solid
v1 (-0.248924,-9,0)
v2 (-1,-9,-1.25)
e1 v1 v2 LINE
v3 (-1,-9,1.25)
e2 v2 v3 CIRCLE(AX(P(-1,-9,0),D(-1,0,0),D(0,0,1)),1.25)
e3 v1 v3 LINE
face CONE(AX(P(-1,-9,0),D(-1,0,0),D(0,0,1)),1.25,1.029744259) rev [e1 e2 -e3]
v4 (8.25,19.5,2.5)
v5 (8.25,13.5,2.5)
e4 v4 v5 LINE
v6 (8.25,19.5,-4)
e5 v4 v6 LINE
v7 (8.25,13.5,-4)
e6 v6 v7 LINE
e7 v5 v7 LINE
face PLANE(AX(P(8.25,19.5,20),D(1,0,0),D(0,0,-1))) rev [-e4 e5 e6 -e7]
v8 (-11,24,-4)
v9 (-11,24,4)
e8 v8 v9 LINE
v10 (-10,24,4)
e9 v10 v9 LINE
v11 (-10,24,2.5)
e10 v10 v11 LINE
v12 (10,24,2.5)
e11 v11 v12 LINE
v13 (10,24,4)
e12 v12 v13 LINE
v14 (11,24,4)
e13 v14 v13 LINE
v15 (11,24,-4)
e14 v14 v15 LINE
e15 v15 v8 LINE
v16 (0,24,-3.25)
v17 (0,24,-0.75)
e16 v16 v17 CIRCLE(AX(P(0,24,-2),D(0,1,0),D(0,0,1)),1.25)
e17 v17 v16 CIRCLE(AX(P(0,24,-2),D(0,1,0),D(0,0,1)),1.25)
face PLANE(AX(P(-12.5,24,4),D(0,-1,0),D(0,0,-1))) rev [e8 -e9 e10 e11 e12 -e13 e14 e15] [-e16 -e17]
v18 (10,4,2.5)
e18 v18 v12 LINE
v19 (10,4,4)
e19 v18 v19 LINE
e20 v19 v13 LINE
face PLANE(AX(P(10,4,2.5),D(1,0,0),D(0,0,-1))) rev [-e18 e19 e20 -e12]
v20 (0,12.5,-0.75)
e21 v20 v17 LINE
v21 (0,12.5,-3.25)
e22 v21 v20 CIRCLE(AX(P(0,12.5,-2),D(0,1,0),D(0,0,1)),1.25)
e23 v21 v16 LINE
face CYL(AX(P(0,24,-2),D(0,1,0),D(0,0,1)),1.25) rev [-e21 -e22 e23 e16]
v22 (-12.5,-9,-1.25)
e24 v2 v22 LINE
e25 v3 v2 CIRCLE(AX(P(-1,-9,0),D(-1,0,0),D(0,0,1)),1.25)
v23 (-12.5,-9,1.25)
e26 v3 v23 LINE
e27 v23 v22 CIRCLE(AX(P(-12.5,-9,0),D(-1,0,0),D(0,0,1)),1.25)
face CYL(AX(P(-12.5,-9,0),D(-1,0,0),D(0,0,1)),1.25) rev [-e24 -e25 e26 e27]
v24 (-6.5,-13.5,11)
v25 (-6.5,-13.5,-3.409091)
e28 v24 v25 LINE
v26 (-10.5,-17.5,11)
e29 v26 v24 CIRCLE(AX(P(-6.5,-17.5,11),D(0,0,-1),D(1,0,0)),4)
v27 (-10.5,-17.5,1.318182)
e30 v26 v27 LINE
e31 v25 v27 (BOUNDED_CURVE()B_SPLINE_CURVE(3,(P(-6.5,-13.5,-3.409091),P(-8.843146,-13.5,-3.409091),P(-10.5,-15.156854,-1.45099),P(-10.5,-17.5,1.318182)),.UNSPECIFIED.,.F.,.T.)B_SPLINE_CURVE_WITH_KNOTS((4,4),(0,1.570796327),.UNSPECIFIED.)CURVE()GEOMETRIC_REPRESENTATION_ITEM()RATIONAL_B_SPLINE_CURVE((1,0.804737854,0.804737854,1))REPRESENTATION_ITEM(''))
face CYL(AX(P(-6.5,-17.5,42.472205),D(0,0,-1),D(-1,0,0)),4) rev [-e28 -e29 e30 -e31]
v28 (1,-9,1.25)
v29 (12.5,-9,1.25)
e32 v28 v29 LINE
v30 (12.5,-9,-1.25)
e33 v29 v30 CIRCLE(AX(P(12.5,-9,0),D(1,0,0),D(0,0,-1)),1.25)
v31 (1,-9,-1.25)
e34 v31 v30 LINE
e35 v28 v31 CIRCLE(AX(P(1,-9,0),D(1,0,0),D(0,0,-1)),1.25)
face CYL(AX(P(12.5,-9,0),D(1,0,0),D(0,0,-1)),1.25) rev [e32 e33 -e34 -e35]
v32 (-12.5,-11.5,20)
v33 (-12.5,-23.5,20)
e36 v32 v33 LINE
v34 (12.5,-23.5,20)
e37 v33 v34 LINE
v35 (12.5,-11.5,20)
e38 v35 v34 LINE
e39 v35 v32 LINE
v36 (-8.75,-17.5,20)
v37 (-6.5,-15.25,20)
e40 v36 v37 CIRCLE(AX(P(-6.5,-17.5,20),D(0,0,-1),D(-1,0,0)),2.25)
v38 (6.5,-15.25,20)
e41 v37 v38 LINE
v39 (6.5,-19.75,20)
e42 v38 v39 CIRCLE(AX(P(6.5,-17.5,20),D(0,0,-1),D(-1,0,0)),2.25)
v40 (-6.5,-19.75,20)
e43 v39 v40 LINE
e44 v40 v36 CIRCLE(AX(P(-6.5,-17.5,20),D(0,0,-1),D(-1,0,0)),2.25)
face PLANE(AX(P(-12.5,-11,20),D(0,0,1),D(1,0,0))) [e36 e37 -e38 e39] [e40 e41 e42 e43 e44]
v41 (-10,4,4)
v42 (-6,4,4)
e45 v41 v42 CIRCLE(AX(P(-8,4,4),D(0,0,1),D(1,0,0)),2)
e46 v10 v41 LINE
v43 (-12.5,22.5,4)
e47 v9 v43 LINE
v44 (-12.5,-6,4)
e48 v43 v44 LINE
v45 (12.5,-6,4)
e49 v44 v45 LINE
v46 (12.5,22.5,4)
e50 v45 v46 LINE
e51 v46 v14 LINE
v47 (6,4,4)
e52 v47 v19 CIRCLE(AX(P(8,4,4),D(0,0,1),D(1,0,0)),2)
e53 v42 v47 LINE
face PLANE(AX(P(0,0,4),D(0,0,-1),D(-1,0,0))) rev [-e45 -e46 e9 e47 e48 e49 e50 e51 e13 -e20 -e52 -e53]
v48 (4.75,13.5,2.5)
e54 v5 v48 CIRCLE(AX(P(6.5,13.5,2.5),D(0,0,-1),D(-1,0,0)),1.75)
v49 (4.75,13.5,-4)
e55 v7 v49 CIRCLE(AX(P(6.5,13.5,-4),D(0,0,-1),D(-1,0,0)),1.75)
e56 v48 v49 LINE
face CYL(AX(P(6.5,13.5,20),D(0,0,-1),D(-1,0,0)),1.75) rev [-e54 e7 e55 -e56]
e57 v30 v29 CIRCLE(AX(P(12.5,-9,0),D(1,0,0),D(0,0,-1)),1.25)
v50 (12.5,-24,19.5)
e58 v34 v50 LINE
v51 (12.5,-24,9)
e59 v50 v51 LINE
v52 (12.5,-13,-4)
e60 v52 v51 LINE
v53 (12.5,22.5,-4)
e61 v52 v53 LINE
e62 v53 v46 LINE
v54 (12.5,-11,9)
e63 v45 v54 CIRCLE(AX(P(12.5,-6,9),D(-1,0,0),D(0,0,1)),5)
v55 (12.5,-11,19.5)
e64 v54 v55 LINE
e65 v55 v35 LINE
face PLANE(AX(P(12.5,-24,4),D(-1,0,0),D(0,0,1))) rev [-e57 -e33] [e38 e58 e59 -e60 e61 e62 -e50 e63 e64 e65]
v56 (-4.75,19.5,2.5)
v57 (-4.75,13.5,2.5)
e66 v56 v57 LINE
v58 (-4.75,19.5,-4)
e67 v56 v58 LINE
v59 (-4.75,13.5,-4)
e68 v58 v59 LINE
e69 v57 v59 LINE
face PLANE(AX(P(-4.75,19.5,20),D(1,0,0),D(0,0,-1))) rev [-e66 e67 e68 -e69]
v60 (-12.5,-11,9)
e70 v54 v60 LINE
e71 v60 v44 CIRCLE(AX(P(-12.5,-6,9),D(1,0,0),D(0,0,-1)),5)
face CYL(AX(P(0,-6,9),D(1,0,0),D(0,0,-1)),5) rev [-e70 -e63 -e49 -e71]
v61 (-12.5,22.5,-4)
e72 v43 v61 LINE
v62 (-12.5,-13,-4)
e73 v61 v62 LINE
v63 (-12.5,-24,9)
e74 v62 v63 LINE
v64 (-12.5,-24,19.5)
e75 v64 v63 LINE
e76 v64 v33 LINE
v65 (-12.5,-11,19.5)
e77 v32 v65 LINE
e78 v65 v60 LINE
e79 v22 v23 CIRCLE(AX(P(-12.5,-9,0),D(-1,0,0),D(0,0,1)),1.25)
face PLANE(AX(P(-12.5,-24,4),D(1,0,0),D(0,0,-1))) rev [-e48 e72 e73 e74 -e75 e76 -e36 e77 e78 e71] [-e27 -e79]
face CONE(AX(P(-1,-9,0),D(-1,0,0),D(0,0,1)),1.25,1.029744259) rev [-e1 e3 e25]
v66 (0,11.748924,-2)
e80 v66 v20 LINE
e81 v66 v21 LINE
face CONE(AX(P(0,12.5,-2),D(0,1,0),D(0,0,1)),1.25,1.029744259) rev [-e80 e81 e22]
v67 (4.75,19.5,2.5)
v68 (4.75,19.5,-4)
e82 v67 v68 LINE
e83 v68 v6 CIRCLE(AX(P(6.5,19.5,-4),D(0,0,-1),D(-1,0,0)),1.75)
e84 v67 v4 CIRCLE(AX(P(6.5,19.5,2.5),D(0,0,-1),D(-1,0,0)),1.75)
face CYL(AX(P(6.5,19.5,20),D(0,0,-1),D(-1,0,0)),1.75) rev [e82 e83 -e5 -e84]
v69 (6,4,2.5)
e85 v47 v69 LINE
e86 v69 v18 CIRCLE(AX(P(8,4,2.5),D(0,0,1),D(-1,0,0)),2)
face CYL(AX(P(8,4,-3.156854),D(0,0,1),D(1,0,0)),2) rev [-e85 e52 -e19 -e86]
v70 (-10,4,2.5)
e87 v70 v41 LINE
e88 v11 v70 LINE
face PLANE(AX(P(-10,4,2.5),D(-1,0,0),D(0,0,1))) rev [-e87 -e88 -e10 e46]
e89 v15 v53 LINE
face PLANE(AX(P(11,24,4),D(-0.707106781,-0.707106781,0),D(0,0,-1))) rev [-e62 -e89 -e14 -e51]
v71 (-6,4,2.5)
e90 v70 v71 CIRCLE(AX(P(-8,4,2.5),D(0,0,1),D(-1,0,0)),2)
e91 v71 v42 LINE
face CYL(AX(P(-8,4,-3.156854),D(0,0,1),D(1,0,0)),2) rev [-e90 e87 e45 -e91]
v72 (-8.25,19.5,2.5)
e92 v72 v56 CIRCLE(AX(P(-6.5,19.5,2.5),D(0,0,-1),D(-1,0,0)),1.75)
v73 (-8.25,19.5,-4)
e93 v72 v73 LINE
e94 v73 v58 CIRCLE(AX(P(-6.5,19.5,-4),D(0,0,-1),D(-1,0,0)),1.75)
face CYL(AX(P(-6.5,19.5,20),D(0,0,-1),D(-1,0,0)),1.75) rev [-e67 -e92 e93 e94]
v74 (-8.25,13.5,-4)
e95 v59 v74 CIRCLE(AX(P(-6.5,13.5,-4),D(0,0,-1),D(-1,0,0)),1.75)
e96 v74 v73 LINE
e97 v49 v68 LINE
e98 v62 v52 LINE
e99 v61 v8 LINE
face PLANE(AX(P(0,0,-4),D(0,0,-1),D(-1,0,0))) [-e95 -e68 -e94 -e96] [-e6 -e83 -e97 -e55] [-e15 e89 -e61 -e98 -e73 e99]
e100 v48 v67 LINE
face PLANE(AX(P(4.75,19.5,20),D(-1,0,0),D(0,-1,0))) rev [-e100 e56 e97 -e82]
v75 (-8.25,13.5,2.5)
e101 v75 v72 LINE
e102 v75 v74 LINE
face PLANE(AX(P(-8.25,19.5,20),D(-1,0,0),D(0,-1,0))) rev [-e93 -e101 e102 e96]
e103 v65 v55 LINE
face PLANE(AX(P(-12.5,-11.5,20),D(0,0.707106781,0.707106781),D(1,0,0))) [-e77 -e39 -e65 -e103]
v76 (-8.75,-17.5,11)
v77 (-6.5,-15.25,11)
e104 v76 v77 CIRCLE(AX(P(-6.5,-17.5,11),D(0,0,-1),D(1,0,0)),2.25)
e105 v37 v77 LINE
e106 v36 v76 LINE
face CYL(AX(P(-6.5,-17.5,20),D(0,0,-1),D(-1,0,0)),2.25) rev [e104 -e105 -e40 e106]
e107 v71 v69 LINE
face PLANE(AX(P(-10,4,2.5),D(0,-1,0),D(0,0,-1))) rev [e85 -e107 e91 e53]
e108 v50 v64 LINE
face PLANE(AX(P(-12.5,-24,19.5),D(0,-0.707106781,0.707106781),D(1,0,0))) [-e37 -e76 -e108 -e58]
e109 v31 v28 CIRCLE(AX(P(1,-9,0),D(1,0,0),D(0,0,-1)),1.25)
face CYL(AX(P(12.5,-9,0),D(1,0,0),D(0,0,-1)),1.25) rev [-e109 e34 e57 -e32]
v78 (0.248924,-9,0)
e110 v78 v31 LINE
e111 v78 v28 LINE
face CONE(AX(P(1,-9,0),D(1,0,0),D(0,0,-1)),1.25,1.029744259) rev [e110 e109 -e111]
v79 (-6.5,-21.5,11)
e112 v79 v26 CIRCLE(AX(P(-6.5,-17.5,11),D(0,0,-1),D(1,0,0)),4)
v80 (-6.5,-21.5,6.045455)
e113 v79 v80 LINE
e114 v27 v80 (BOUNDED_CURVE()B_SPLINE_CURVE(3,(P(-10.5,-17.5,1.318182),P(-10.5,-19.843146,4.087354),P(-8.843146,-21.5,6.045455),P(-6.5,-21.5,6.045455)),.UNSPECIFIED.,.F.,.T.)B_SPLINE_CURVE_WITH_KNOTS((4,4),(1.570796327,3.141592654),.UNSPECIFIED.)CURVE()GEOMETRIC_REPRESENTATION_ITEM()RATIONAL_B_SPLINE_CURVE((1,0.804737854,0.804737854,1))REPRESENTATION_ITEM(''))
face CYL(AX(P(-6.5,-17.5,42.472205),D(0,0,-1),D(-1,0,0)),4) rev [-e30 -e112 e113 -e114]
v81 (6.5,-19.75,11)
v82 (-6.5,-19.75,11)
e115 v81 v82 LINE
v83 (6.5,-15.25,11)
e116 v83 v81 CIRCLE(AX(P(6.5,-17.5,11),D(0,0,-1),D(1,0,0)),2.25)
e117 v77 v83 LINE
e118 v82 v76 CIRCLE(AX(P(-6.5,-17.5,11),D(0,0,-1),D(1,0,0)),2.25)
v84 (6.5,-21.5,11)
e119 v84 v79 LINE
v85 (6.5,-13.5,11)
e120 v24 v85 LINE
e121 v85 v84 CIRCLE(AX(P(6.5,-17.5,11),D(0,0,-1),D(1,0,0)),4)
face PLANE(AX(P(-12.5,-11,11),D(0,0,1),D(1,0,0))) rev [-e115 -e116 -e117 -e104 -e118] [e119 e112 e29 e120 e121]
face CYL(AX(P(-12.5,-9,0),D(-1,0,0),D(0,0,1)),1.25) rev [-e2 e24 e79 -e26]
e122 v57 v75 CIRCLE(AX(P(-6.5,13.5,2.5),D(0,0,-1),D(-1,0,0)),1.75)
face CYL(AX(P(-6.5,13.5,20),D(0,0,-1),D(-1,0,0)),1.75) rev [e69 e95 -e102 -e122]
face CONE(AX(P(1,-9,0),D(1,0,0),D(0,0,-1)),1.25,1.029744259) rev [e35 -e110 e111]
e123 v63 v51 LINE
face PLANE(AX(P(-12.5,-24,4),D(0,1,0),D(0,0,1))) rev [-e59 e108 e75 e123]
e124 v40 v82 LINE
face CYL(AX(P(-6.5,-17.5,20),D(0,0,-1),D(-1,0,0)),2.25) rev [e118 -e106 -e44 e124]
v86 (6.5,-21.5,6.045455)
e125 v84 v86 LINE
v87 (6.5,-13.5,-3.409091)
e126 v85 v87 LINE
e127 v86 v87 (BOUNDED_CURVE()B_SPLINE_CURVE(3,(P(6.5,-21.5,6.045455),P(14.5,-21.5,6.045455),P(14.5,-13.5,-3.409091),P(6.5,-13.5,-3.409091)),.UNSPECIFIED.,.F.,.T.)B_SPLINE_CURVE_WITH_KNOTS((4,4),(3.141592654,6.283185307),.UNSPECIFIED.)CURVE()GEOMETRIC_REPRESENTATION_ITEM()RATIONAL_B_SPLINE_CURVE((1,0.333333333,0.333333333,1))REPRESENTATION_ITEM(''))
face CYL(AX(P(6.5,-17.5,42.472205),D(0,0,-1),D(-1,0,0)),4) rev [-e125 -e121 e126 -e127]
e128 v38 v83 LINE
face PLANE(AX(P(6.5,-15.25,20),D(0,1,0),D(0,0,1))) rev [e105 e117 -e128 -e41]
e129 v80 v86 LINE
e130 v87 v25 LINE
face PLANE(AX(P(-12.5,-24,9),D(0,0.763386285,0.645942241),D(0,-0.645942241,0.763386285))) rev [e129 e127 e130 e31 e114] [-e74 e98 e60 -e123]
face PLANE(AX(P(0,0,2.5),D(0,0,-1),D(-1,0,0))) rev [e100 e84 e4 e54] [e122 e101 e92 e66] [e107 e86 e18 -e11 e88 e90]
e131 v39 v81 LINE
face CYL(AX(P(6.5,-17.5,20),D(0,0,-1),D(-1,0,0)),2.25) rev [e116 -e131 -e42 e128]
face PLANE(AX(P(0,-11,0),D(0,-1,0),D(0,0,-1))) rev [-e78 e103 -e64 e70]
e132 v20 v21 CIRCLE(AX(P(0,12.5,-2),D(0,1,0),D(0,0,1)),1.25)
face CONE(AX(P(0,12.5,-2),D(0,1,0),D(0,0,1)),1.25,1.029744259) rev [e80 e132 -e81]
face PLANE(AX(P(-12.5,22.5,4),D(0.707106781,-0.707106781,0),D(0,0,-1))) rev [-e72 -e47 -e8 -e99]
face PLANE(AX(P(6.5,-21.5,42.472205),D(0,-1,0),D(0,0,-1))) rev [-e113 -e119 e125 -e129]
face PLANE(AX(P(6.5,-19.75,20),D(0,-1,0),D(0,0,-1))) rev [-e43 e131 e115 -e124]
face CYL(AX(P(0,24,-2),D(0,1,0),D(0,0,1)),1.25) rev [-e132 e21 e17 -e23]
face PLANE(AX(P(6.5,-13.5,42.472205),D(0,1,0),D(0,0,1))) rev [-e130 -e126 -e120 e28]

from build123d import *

# Parameters (mm, degrees)
SKETCH1_W             = 25
SKETCH1_H             = 48
BOSS_EXTRUDE1_DEPTH   = 4
SKETCH5_W             = 25
SKETCH5_H             = 24
BOSS_EXTRUDE3_DEPTH   = 13
SKETCH6_W             = 20
SKETCH6_H             = 40
CUT_EXTRUDE1_DEPTH    = 1.5
M3_TAPPED_HOLE1_D     = 2.5
M3_TAPPED_HOLE1_DEPTH = 11.5
M3_TAPPED_HOLE1_TIP   = 0.751075774
CHAMFER2_SIZE         = 1.5
CUT_EXTRUDE3_DEPTH    = 37.169738733
SKETCH18_R            = 2
CUT_EXTRUDE5_DEPTH    = 1.5
CUT_EXTRUDE6_DEPTH    = 37.169738733
CUT_EXTRUDE7_DEPTH    = 41.012498047
CUT_EXTRUDE8_DEPTH    = 15
FILLET2_R             = 5
CHAMFER4_SIZE         = 0.5


with BuildPart() as part:
    # Sketch1 → Boss-Extrude1 (new, symmetric)
    with BuildSketch(Plane.XY):
        Rectangle(SKETCH1_W, SKETCH1_H)
    extrude(amount=BOSS_EXTRUDE1_DEPTH, both=True)

    # Sketch5 → Boss-Extrude3 (add)
    with BuildSketch(Plane.XZ.offset(24)):
        with Locations((0, 8)):
            Rectangle(SKETCH5_W, SKETCH5_H)
    extrude(amount=-BOSS_EXTRUDE3_DEPTH)

    # Sketch6 → Cut-Extrude1 (cut)
    with BuildSketch(Plane.XY.offset(4)):
        with Locations((0, 24)):
            Rectangle(SKETCH6_W, SKETCH6_H)
    extrude(amount=-CUT_EXTRUDE1_DEPTH, mode=Mode.SUBTRACT)

    # M3 Tapped Hole1
    with Locations(Plane(origin=(0, 24, 0), x_dir=(1, 0, 0), z_dir=(0, 1, 0))):
        with Locations((0, 2)):
            Hole(M3_TAPPED_HOLE1_D / 2, depth=M3_TAPPED_HOLE1_DEPTH)
            with Locations((0, 0, -(M3_TAPPED_HOLE1_DEPTH + M3_TAPPED_HOLE1_TIP / 2))):  # 118° drill point
                Cone(0, M3_TAPPED_HOLE1_D / 2, M3_TAPPED_HOLE1_TIP, mode=Mode.SUBTRACT)

    # Chamfer2
    chamfer2_edges = [part.edges().sort_by_distance(p)[0] for p in [
        (-12.5, 24, 0),
        (12.5, 24, 0),
    ]]
    chamfer(chamfer2_edges, length=CHAMFER2_SIZE)

    # Sketch14 → Cut-Extrude3 (cut, through all)
    with BuildSketch(Plane(origin=(0, 0, -4), x_dir=(-1, 0, 0), z_dir=(0, 0, -1))):
        with BuildLine():
            Line((-4.75, 19.5), (-4.75, 13.5))
            ThreePointArc((-4.75, 13.5), (-6.5, 11.75), (-8.25, 13.5))
            Line((-8.25, 13.5), (-8.25, 19.5))
            ThreePointArc((-8.25, 19.5), (-6.5, 21.25), (-4.75, 19.5))
        make_face()
        with BuildLine():
            Line((8.25, 19.5), (8.25, 13.5))
            ThreePointArc((8.25, 13.5), (6.5, 11.75), (4.75, 13.5))
            Line((4.75, 13.5), (4.75, 19.5))
            ThreePointArc((4.75, 19.5), (6.5, 21.25), (8.25, 19.5))
        make_face()
    extrude(amount=-CUT_EXTRUDE3_DEPTH, mode=Mode.SUBTRACT)

    # Sketch15 → M3 Tapped Hole2 (revolve, cut)
    with BuildSketch(Plane(origin=(-12.5, -9, 0), x_dir=(0, 0, 1), z_dir=(0, 1, 0))):
        Polygon((0, 0), (0, 12.251075774), (1.25, 11.5), (1.25, 0), align=None)
    m3_tapped_hole2 = revolve(axis=Axis((-18.85, -9, 0), (1, 0, 0)), mode=Mode.SUBTRACT)

    # Sketch18 → Cut-Extrude5 (cut)
    with BuildSketch(Plane.XY.offset(4)):
        with Locations((-8, 4)):
            Circle(SKETCH18_R)
        with Locations((8, 4)):
            Circle(SKETCH18_R)
    extrude(amount=-CUT_EXTRUDE5_DEPTH, mode=Mode.SUBTRACT)

    # Sketch20 → Cut-Extrude6 (cut, through all)
    with BuildSketch(Plane(origin=(0, 0, -4), x_dir=(-1, 0, 0), z_dir=(0, 0, -1))):
        with BuildLine():
            Line((-6.5, -15.25), (6.5, -15.25))
            ThreePointArc((6.5, -15.25), (8.75, -17.5), (6.5, -19.75))
            Line((6.5, -19.75), (-6.5, -19.75))
            ThreePointArc((-6.5, -19.75), (-8.75, -17.5), (-6.5, -15.25))
        make_face()
    extrude(amount=-CUT_EXTRUDE6_DEPTH, mode=Mode.SUBTRACT)

    # Sketch21 → Cut-Extrude7 (cut, through all)
    with BuildSketch(Plane(origin=(12.5, 0, 0), x_dir=(0, 0, -1), z_dir=(1, 0, 0))):
        Polygon((-9, -24), (4, -13), (4, -24), align=None)
    extrude(amount=-CUT_EXTRUDE7_DEPTH, mode=Mode.SUBTRACT)

    # Sketch22 → Cut-Extrude8 (cut)
    with BuildSketch(Plane(origin=(0, 0, -4), x_dir=(-1, 0, 0), z_dir=(0, 0, -1))):
        with BuildLine():
            Line((-6.5, -13.5), (6.5, -13.5))
            ThreePointArc((6.5, -13.5), (10.5, -17.5), (6.5, -21.5))
            Line((6.5, -21.5), (-6.5, -21.5))
            ThreePointArc((-6.5, -21.5), (-10.5, -17.5), (-6.5, -13.5))
        make_face()
    extrude(amount=-CUT_EXTRUDE8_DEPTH, mode=Mode.SUBTRACT)

    # Fillet2
    fillet2_edges = [part.edges().sort_by_distance(p)[0] for p in [
        (0, -11, 4),
    ]]
    fillet(fillet2_edges, radius=FILLET2_R)

    # Mirror1: M3 Tapped Hole2 across plane
    add(m3_tapped_hole2.mirror(Plane(origin=(0, 0, 0), x_dir=(0, 0, 1), z_dir=(1, 0, 0))), mode=Mode.SUBTRACT)

    # Chamfer4
    chamfer4_edges = [part.edges().sort_by_distance(p)[0] for p in [
        (0, -24, 20),
        (0, -11, 20),
    ]]
    chamfer(chamfer4_edges, length=CHAMFER4_SIZE)


solid = part.part
